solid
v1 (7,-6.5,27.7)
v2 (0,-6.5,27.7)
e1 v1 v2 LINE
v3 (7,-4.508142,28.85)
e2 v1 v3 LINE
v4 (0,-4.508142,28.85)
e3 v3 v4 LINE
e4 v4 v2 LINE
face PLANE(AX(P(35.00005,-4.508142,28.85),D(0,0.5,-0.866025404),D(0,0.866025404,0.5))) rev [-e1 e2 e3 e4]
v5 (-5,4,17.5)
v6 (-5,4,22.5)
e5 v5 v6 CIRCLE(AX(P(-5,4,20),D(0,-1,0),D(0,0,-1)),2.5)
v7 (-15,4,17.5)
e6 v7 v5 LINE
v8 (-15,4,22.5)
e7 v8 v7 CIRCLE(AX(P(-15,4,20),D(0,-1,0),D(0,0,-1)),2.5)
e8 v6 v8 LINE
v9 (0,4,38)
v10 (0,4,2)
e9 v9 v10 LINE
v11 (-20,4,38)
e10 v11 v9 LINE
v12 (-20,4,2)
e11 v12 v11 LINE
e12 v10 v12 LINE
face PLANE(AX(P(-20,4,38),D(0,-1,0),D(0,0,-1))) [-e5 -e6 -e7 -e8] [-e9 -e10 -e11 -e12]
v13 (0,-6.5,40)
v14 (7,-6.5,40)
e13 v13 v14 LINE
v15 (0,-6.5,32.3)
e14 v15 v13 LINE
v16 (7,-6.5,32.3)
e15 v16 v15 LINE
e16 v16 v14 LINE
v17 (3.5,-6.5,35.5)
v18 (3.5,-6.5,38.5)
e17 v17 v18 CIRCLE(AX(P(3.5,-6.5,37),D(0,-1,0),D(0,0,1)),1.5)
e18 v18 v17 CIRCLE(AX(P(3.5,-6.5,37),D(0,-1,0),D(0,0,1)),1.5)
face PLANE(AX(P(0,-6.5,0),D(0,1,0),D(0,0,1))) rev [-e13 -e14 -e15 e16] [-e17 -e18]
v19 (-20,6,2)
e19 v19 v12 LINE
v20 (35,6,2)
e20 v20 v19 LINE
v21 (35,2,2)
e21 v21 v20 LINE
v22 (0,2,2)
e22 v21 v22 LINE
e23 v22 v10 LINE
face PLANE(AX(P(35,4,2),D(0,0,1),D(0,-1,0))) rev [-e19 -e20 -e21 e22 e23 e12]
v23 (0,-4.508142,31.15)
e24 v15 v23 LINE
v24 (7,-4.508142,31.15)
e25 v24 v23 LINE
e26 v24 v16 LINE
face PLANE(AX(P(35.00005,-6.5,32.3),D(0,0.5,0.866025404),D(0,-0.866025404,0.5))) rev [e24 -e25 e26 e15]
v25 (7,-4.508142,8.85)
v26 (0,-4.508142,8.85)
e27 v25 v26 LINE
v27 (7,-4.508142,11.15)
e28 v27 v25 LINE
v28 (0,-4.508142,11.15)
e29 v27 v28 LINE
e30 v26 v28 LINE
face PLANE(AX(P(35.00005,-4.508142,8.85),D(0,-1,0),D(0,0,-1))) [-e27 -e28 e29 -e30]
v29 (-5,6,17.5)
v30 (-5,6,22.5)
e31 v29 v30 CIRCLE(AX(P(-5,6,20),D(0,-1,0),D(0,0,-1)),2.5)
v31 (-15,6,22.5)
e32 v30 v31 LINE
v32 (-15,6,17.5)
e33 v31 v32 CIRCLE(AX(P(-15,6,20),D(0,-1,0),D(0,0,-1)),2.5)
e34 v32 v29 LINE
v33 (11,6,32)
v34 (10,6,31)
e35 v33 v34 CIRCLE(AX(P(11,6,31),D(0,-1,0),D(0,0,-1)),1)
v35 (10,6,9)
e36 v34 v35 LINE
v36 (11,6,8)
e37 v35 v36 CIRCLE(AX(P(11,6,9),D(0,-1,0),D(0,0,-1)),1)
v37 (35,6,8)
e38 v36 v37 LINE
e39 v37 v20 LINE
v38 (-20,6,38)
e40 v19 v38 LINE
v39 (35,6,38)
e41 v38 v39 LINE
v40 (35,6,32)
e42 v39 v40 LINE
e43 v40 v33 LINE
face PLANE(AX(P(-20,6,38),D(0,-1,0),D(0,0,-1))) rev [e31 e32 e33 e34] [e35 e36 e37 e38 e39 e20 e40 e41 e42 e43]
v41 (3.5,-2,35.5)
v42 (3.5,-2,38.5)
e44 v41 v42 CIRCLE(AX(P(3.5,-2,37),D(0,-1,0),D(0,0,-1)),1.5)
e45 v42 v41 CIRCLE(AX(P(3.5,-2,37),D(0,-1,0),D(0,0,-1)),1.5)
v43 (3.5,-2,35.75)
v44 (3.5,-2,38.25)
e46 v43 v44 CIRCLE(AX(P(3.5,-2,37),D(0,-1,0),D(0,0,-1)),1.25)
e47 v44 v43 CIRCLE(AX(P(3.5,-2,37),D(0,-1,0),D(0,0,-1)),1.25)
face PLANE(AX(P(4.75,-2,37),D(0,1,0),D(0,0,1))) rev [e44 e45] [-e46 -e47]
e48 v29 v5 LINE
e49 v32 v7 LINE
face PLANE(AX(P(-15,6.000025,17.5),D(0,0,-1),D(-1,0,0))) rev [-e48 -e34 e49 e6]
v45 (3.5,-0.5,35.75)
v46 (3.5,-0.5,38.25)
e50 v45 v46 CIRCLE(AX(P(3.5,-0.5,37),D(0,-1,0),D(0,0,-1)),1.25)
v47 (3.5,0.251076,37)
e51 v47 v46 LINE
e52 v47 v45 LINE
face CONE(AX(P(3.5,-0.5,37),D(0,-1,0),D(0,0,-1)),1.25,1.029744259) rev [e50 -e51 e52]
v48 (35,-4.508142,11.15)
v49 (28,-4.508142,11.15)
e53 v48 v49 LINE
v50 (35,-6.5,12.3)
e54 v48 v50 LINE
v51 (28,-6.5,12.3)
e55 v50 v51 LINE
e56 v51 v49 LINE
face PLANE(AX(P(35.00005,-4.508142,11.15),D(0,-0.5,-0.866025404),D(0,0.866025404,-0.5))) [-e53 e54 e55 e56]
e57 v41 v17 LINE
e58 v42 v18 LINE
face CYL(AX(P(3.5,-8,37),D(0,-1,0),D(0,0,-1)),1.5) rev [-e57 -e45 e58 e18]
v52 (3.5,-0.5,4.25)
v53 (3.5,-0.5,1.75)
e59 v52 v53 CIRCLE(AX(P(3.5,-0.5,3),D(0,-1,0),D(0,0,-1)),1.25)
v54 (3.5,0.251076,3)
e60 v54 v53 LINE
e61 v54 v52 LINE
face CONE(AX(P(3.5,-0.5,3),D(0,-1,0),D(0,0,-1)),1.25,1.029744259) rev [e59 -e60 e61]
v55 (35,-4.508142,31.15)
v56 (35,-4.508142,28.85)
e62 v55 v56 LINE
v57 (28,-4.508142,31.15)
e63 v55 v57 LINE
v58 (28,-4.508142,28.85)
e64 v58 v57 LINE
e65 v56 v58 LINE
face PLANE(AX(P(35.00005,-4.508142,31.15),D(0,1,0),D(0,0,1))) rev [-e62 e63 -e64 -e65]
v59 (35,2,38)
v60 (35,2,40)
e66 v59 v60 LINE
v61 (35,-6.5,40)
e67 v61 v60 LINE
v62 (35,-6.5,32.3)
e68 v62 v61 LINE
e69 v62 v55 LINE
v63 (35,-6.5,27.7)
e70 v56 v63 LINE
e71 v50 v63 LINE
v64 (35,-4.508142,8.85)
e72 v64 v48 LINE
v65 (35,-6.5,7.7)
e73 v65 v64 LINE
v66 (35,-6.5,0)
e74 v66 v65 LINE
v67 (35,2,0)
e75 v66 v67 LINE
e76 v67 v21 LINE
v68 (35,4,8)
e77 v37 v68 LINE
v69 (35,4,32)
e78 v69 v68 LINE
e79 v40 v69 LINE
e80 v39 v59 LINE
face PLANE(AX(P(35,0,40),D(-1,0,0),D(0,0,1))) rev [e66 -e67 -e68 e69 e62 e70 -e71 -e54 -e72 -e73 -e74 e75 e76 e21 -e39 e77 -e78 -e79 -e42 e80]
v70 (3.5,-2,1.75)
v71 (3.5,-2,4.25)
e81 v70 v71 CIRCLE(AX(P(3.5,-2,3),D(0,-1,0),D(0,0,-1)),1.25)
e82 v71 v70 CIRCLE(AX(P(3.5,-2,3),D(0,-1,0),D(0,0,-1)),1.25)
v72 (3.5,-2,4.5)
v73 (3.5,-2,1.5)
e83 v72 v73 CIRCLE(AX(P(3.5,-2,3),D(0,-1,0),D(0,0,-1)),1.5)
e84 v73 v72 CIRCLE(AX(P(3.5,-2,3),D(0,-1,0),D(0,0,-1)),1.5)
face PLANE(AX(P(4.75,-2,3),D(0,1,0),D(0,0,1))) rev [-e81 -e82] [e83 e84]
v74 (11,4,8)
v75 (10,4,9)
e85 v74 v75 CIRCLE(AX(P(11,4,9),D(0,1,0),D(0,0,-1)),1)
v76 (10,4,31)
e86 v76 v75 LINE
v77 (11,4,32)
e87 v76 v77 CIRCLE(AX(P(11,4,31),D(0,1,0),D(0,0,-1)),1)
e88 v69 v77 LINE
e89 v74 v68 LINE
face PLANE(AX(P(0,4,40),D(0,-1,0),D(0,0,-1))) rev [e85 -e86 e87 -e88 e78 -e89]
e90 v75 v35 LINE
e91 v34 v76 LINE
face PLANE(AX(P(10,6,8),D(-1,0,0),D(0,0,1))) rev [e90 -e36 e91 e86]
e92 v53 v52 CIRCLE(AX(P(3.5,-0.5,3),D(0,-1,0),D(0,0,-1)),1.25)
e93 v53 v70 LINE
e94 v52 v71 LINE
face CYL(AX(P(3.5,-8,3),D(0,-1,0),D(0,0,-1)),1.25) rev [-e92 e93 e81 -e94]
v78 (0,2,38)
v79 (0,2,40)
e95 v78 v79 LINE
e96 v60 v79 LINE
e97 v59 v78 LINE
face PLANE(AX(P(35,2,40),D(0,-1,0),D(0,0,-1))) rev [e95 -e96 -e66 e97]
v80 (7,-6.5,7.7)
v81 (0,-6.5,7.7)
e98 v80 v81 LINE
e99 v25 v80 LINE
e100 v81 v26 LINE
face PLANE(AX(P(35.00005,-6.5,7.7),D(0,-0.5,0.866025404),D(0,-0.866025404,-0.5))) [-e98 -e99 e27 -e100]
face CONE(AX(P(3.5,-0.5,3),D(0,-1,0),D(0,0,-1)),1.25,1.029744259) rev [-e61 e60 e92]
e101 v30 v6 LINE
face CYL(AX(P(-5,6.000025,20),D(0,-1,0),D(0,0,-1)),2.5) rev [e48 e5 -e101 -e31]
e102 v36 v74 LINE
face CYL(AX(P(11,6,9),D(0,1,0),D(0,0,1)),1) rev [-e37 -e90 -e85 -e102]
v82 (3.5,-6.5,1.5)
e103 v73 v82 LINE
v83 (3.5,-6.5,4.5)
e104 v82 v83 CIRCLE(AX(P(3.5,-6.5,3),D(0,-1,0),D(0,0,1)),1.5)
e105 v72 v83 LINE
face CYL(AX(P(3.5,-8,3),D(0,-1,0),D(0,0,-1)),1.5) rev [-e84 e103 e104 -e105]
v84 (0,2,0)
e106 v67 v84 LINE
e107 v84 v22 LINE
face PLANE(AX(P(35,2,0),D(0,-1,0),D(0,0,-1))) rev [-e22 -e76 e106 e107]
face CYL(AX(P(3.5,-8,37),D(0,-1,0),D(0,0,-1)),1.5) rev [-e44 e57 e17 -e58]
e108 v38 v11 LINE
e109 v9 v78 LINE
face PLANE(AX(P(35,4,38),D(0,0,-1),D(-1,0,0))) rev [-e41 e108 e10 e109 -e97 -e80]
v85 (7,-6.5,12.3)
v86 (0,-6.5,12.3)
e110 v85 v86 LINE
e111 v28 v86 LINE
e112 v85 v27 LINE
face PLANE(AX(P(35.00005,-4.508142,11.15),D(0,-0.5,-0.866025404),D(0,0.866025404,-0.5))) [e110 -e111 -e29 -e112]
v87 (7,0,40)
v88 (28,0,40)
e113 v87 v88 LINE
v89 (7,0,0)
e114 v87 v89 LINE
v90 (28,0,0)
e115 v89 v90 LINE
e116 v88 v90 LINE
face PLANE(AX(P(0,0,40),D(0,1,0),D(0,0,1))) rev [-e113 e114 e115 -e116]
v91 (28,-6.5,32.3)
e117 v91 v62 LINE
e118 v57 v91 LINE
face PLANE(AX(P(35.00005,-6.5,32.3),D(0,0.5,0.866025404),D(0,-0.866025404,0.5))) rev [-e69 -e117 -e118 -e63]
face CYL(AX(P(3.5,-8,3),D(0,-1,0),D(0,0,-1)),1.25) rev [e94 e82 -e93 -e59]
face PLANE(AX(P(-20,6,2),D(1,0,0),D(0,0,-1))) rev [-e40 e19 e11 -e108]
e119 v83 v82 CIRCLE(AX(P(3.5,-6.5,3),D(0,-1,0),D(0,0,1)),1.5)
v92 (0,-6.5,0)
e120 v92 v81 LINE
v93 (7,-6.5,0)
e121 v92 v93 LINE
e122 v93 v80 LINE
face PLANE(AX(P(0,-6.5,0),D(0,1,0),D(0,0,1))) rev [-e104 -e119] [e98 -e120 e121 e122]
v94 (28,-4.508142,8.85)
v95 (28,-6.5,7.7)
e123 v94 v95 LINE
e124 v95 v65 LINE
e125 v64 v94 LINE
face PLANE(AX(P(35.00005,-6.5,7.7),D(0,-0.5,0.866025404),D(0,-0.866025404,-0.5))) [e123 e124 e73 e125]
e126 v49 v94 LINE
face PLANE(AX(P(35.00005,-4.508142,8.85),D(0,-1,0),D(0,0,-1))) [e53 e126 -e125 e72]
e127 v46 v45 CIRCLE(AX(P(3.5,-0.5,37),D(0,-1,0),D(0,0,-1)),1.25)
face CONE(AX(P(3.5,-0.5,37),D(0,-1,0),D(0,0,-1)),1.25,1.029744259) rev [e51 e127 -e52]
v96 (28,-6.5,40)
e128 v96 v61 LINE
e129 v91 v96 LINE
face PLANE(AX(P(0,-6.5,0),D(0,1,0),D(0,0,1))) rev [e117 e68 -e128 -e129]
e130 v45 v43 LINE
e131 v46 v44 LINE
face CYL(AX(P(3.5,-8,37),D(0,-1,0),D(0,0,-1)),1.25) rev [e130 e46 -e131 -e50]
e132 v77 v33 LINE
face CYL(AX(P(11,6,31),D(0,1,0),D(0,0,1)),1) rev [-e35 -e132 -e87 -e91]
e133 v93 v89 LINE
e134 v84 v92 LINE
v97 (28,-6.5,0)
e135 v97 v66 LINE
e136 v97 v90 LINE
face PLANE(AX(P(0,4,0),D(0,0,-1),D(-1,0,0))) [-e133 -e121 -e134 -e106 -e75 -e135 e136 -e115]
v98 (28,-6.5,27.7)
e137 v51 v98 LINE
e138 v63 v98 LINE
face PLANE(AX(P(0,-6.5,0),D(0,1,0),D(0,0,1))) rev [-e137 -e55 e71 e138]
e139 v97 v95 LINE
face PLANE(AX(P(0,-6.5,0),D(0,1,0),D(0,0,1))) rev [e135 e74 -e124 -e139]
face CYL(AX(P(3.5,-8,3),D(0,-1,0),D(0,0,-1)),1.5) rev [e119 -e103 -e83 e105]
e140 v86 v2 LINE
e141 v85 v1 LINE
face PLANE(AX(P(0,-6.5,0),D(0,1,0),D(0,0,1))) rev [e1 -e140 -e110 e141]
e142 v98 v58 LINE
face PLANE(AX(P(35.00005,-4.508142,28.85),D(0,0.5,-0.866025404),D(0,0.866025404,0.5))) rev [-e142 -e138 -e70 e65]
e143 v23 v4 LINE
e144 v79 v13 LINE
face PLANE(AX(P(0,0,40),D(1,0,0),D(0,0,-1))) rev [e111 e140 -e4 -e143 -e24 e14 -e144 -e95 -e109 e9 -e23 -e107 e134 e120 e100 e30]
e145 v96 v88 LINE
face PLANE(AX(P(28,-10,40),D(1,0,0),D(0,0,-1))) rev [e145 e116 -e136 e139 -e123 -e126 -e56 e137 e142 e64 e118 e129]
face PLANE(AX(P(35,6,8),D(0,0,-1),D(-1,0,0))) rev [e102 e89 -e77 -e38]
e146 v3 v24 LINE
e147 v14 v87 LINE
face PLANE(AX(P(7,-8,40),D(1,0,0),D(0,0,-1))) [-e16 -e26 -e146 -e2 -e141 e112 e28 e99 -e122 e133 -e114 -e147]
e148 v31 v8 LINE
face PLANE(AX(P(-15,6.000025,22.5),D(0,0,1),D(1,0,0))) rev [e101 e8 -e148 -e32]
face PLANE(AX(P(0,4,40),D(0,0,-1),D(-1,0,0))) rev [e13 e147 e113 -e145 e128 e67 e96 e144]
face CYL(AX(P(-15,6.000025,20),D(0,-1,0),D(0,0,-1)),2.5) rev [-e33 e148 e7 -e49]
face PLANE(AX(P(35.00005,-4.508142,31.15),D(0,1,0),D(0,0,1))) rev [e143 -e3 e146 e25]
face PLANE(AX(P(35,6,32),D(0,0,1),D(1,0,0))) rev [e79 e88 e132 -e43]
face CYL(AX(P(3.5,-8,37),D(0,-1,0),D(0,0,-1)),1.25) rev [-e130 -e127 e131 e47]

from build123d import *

# Parameters (mm, degrees)
SKETCH_1_W                   = 35
SKETCH_1_H                   = 4
EXTRUDE_1_DEPTH              = 40
SKETCH_2_W                   = 7
SKETCH_2_H                   = 40
EXTRUDE_2_DEPTH              = 12
HOLE_WIZARD_M3_1_D           = 2.5
HOLE_WIZARD_M3_1_DEPTH       = 7.5
HOLE_WIZARD_M3_1_CBORE_D     = 3
HOLE_WIZARD_M3_1_CBORE_DEPTH = 6
HOLE_WIZARD_M3_1_TIP         = 0.751075774
SKETCH_9_W                   = 7
SKETCH_9_H                   = 40
EXTRUDE_3_DEPTH              = 10
SKETCH_14_W                  = 40
SKETCH_14_H                  = 3.5
CUT_EXTRUDE_5_DEPTH          = 55.083269132
SKETCH_15_W                  = 2
SKETCH_15_H                  = 2
CUT_EXTRUDE_6_DEPTH          = 54.546708582
EXTRUDE_5_DEPTH              = 2
CUT_EXTRUDE_7_DEPTH          = 54.546708582
FILLET_1_R                   = 1
CUT_EXTRUDE_8_DEPTH          = 55.177947543


with BuildPart() as part:
    # 草图1 → 拉伸1 (new body)
    with BuildSketch(Plane.XY):
        with Locations((17.5, 2)):
            Rectangle(SKETCH_1_W, SKETCH_1_H)
    extrude(amount=EXTRUDE_1_DEPTH)

    # 草图2 → 拉伸2 (add)
    with BuildSketch(Plane(origin=(0, 4, 0), x_dir=(-1, 0, 0), z_dir=(0, 1, 0))):
        with Locations((-3.5, 20)):
            Rectangle(SKETCH_2_W, SKETCH_2_H)
    extrude(amount=-EXTRUDE_2_DEPTH)

    # M3 螺纹孔1
    with Locations(Plane.XZ.offset(8)):
        with Locations((3.5, 3), (3.5, 37)):
            CounterBoreHole(HOLE_WIZARD_M3_1_D / 2, HOLE_WIZARD_M3_1_CBORE_D / 2, HOLE_WIZARD_M3_1_CBORE_DEPTH, depth=HOLE_WIZARD_M3_1_DEPTH)
            with Locations((0, 0, -(HOLE_WIZARD_M3_1_DEPTH + HOLE_WIZARD_M3_1_TIP / 2))):  # 118° drill point
                Cone(0, HOLE_WIZARD_M3_1_D / 2, HOLE_WIZARD_M3_1_TIP, mode=Mode.SUBTRACT)

    # 草图9 → 拉伸3 (add)
    with BuildSketch(Plane.XZ):
        with Locations((31.5, 20)):
            Rectangle(SKETCH_9_W, SKETCH_9_H)
    extrude(amount=EXTRUDE_3_DEPTH)

    # 草图14 → 切除-拉伸5 (cut, through all)
    with BuildSketch(Plane(origin=(35, 0, 0), x_dir=(0, 0, -1), z_dir=(1, 0, 0))):
        with Locations((-20, -8.25)):
            Rectangle(SKETCH_14_W, SKETCH_14_H)
    extrude(amount=-CUT_EXTRUDE_5_DEPTH, mode=Mode.SUBTRACT)

    # 草图15 → 切除-拉伸6 (cut, through all)
    with BuildSketch(Plane.ZY):
        with Locations((1, 3)):
            Rectangle(SKETCH_15_W, SKETCH_15_H)
        with Locations((39, 3)):
            Rectangle(SKETCH_15_W, SKETCH_15_H)
    extrude(amount=-CUT_EXTRUDE_6_DEPTH, mode=Mode.SUBTRACT)

    # 草图17 → 拉伸5 (add)
    with BuildSketch(Plane(origin=(0, 4, 0), x_dir=(1, 0, 0), z_dir=(0, 1, 0))):
        Polygon((-20, -2), (35, -2), (35, -8), (10, -8), (10, -32), (35, -32), (35, -38), (-20, -38), align=None)
    extrude(amount=EXTRUDE_5_DEPTH)

    # 草图18 → 切除-拉伸7 (cut, through all)
    with BuildSketch(Plane.ZY):
        Polygon((31.15, -4.508141571), (28.85, -4.508141571), (27.7, -6.5), (28.85, -8.491858429), (31.15, -8.491858429), (32.3, -6.5), align=None)
    cut_extrude_7 = extrude(amount=-CUT_EXTRUDE_7_DEPTH, mode=Mode.SUBTRACT)

    # 镜向1: 切除-拉伸7 across plane
    add(cut_extrude_7.mirror(Plane(origin=(0, 0, 20), x_dir=(1, 0, 0), z_dir=(0, 0, -1))), mode=Mode.SUBTRACT)

    # 圆角1
    fillet_1_edges = [part.edges().sort_by_distance(p)[0] for p in [
        (10, 5, 32),
        (10, 5, 8),
    ]]
    fillet(fillet_1_edges, radius=FILLET_1_R)

    # 草图20 → 切除-拉伸8 (cut, through all)
    with BuildSketch(Plane.XZ.offset(-4)):
        with BuildLine():
            Line((-15, 22.5), (-5, 22.5))
            ThreePointArc((-5, 22.5), (-2.5, 20), (-5, 17.5))
            Line((-5, 17.5), (-15, 17.5))
            ThreePointArc((-15, 17.5), (-17.5, 20), (-15, 22.5))
        make_face()
    extrude(amount=-CUT_EXTRUDE_8_DEPTH, mode=Mode.SUBTRACT)


solid = part.part
